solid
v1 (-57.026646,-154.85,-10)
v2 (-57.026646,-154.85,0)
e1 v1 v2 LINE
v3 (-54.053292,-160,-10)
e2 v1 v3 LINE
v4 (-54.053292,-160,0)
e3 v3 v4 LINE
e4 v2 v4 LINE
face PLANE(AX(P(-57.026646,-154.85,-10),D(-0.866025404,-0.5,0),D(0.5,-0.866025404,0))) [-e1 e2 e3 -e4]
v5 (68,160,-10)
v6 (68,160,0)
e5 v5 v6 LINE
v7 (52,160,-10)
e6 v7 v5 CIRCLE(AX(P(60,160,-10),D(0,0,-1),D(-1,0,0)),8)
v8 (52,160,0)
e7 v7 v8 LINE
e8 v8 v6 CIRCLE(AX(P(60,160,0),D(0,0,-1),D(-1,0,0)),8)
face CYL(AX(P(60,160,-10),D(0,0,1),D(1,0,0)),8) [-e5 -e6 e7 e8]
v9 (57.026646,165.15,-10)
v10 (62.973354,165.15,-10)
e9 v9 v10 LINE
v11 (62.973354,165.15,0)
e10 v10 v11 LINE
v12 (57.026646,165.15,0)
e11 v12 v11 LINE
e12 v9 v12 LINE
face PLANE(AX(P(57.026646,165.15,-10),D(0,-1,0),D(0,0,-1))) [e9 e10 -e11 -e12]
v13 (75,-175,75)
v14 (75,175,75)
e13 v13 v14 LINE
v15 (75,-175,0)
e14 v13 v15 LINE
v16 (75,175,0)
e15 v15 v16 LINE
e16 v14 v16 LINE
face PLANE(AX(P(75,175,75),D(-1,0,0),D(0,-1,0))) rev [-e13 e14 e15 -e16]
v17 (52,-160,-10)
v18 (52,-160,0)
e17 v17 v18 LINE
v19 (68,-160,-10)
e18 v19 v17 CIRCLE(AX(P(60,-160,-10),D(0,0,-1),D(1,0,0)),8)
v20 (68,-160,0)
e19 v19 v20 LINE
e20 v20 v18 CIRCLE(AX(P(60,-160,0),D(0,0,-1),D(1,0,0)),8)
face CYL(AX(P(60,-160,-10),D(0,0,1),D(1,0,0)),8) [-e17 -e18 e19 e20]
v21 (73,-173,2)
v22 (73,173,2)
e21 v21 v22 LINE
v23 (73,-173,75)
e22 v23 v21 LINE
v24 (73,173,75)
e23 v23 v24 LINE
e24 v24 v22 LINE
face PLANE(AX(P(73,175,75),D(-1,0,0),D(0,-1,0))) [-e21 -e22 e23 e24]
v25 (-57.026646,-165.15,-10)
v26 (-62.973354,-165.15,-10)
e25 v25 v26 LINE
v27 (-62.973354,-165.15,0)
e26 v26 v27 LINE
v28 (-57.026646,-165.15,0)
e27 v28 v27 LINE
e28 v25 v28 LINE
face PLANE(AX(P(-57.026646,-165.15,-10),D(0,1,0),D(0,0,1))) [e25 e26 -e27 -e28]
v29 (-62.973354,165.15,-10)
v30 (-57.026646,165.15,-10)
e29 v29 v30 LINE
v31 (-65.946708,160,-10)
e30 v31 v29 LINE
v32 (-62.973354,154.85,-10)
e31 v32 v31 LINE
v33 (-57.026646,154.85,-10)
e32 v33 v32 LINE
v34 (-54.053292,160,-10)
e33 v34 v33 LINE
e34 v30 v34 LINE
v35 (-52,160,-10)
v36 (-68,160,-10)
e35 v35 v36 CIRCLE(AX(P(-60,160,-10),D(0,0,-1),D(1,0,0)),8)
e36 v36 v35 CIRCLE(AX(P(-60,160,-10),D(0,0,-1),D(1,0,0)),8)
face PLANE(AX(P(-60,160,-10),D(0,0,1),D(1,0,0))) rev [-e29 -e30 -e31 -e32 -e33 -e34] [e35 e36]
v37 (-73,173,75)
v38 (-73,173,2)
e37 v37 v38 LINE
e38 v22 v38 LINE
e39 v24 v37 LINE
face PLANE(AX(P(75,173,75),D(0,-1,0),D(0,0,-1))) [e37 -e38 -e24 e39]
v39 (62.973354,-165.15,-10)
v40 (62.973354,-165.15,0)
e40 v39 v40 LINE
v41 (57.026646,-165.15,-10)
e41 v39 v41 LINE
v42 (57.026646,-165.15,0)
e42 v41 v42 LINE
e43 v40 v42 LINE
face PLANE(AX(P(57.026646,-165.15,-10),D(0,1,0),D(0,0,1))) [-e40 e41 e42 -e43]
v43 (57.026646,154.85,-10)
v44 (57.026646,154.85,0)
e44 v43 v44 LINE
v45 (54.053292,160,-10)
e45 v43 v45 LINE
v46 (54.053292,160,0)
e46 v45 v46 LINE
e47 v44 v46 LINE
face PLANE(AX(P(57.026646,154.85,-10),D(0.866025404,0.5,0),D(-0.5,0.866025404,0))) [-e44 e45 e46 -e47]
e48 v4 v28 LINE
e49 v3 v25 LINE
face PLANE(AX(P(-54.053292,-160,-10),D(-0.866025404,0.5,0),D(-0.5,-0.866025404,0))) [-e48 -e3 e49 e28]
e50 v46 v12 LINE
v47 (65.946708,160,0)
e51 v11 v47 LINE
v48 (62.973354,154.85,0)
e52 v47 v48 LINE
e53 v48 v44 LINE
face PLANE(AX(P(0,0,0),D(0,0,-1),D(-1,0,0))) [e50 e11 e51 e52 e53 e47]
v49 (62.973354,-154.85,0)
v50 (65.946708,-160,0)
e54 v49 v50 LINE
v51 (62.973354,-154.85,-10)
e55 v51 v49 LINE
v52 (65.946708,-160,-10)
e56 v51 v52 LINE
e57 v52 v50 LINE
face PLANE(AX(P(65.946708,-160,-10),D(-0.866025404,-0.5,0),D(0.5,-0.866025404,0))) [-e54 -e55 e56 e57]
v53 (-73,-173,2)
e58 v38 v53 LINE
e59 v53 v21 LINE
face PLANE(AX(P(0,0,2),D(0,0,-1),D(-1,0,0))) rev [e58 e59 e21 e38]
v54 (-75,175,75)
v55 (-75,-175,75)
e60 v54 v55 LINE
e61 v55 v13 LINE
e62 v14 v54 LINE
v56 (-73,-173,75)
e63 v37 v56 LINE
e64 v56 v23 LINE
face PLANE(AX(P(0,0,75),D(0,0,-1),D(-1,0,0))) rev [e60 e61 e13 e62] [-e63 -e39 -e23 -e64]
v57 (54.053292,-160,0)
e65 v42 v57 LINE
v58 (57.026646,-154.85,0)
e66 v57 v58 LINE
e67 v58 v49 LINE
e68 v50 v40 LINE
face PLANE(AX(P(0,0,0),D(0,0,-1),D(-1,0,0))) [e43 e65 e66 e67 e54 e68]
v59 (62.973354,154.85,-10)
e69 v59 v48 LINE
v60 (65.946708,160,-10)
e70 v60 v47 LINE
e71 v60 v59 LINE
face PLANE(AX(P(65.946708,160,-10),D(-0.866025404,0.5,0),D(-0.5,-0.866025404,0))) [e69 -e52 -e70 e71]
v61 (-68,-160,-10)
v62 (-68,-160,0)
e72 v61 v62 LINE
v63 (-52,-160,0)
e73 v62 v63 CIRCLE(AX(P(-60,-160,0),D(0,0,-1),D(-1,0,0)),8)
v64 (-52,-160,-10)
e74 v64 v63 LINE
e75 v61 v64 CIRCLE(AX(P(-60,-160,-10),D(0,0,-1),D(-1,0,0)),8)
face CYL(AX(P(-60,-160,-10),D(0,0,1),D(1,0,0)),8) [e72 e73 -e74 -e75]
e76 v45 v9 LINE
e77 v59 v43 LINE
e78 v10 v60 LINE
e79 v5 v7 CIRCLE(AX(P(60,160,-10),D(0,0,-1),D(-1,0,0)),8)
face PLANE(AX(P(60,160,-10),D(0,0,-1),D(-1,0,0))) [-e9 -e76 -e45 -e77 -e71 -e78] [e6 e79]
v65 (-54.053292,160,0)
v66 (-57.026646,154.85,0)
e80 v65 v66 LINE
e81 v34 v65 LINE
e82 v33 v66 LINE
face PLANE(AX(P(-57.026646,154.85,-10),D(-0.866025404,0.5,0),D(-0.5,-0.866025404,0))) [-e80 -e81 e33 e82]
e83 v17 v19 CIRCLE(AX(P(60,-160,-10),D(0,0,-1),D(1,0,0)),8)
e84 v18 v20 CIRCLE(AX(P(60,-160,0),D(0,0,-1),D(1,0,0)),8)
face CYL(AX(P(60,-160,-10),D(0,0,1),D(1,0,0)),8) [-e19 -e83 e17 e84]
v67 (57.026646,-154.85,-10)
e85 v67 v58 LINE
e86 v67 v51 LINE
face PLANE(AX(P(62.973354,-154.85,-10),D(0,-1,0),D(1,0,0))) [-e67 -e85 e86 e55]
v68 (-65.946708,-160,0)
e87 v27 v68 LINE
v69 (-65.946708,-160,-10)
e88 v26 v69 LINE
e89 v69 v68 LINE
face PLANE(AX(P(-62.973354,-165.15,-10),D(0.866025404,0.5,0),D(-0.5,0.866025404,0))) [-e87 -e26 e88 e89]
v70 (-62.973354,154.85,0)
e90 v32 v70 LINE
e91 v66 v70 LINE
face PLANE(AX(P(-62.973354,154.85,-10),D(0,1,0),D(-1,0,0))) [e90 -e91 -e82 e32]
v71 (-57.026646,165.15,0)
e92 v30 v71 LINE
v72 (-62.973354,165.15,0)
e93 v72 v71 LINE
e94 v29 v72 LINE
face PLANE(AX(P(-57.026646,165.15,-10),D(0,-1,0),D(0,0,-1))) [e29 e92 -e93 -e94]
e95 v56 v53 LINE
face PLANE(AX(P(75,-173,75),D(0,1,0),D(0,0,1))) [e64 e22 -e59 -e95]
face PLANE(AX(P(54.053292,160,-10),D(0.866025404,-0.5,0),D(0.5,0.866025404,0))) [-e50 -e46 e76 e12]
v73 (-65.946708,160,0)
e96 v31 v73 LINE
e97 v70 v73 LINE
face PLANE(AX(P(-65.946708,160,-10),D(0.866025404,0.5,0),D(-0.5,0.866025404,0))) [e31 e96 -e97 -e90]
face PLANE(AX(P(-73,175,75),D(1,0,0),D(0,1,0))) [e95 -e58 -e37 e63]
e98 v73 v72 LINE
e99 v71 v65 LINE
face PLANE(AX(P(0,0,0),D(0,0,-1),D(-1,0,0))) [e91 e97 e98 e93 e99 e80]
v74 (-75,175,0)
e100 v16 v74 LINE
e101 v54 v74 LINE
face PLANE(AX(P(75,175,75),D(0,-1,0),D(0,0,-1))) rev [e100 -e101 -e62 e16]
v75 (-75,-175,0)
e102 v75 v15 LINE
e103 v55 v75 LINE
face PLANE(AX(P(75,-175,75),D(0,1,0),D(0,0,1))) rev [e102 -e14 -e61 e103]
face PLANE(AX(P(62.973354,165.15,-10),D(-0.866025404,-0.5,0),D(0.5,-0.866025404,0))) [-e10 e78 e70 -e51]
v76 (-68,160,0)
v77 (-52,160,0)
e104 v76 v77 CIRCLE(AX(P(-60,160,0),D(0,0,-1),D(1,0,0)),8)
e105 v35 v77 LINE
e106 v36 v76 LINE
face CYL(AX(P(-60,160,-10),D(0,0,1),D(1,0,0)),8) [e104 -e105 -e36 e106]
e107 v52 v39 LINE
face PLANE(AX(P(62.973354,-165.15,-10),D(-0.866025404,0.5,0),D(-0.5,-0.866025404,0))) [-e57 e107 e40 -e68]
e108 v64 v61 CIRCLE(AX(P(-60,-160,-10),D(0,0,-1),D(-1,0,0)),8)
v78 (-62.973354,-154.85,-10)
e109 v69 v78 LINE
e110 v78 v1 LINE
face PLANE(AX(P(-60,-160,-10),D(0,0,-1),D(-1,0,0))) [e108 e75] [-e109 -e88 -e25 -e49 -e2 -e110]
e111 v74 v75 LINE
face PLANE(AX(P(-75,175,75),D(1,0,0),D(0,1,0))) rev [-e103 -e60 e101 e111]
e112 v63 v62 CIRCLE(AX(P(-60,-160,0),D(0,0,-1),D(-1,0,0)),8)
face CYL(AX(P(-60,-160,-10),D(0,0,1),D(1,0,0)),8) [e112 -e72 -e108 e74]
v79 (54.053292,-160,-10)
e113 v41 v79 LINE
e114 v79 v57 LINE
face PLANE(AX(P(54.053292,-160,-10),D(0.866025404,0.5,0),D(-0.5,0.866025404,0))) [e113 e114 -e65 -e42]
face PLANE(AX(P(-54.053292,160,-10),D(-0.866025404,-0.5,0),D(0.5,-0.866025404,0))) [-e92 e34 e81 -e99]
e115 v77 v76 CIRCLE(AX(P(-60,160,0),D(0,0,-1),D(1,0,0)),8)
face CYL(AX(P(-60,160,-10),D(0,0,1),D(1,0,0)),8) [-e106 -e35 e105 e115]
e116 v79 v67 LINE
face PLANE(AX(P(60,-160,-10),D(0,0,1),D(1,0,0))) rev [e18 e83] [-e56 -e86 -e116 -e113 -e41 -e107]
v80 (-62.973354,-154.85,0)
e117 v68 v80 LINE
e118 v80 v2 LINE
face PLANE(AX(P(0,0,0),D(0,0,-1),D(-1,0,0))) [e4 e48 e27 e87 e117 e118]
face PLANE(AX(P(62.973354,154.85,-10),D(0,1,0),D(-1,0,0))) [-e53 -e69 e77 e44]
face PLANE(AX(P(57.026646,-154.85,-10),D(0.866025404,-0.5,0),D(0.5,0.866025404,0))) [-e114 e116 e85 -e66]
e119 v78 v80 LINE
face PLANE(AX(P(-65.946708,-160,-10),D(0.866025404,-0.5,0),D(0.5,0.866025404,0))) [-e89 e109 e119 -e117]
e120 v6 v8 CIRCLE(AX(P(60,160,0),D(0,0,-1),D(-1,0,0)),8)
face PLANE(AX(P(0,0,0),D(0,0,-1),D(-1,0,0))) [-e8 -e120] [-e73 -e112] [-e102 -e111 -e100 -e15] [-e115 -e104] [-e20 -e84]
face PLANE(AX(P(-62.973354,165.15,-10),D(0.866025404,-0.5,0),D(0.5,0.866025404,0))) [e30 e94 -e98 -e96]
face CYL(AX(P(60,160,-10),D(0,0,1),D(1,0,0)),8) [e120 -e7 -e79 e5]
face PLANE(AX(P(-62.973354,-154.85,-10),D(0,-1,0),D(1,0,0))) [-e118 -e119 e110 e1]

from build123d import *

# Parameters (mm, degrees)
SKETCH1_W           = 150
SKETCH1_H           = 350
BOSS_EXTRUDE1_DEPTH = 75
SHELL1_T            = -2
SKETCH2_R           = 8
BOSS_EXTRUDE2_DEPTH = 10


with BuildPart() as part:
    # Sketch1 → Boss-Extrude1 (new body)
    with BuildSketch(Plane.XY):
        Rectangle(SKETCH1_W, SKETCH1_H)
    extrude(amount=BOSS_EXTRUDE1_DEPTH)

    # Shell1
    shell1_openings = [part.faces().sort_by_distance(p)[0] for p in [
        (0, 0, 75),
    ]]
    offset(amount=SHELL1_T, openings=shell1_openings, kind=Kind.INTERSECTION)

    # Sketch2 → Boss-Extrude2 (add)
    # profile 1 of 4: a face of its own
    with BuildSketch(Plane(origin=(0, 0, 0), x_dir=(-1, 0, 0), z_dir=(0, 0, -1))):
        with Locations((-60, 160)):
            Circle(SKETCH2_R)
        Polygon((-62.973353886, 154.85), (-57.026646114, 154.85), (-54.053292227, 160), (-57.026646114, 165.15), (-62.973353886, 165.15), (-65.946707773, 160), align=None, mode=Mode.SUBTRACT)
    # profile 2 of 4: a face of its own
    with BuildSketch(Plane(origin=(0, 0, 0), x_dir=(-1, 0, 0), z_dir=(0, 0, -1))):
        with Locations(Location((-60, -160, 0), (0, 0, 180))):
            Circle(SKETCH2_R)
        Polygon((-65.946707773, -160), (-62.973353886, -154.85), (-57.026646114, -154.85), (-54.053292227, -160), (-57.026646114, -165.15), (-62.973353886, -165.15), align=None, mode=Mode.SUBTRACT)
    # profile 3 of 4: a face of its own
    with BuildSketch(Plane(origin=(0, 0, 0), x_dir=(-1, 0, 0), z_dir=(0, 0, -1))):
        with Locations((60, -160)):
            Circle(SKETCH2_R)
        Polygon((62.973353886, -165.15), (65.946707773, -160), (62.973353886, -154.85), (57.026646114, -154.85), (54.053292227, -160), (57.026646114, -165.15), align=None, mode=Mode.SUBTRACT)
    # profile 4 of 4: a face of its own
    with BuildSketch(Plane(origin=(0, 0, 0), x_dir=(-1, 0, 0), z_dir=(0, 0, -1))):
        with Locations(Location((60, 160, 0), (0, 0, 180))):
            Circle(SKETCH2_R)
        Polygon((65.946707773, 160), (62.973353886, 154.85), (57.026646114, 154.85), (54.053292227, 160), (57.026646114, 165.15), (62.973353886, 165.15), align=None, mode=Mode.SUBTRACT)
    extrude(amount=BOSS_EXTRUDE2_DEPTH)


solid = part.part
